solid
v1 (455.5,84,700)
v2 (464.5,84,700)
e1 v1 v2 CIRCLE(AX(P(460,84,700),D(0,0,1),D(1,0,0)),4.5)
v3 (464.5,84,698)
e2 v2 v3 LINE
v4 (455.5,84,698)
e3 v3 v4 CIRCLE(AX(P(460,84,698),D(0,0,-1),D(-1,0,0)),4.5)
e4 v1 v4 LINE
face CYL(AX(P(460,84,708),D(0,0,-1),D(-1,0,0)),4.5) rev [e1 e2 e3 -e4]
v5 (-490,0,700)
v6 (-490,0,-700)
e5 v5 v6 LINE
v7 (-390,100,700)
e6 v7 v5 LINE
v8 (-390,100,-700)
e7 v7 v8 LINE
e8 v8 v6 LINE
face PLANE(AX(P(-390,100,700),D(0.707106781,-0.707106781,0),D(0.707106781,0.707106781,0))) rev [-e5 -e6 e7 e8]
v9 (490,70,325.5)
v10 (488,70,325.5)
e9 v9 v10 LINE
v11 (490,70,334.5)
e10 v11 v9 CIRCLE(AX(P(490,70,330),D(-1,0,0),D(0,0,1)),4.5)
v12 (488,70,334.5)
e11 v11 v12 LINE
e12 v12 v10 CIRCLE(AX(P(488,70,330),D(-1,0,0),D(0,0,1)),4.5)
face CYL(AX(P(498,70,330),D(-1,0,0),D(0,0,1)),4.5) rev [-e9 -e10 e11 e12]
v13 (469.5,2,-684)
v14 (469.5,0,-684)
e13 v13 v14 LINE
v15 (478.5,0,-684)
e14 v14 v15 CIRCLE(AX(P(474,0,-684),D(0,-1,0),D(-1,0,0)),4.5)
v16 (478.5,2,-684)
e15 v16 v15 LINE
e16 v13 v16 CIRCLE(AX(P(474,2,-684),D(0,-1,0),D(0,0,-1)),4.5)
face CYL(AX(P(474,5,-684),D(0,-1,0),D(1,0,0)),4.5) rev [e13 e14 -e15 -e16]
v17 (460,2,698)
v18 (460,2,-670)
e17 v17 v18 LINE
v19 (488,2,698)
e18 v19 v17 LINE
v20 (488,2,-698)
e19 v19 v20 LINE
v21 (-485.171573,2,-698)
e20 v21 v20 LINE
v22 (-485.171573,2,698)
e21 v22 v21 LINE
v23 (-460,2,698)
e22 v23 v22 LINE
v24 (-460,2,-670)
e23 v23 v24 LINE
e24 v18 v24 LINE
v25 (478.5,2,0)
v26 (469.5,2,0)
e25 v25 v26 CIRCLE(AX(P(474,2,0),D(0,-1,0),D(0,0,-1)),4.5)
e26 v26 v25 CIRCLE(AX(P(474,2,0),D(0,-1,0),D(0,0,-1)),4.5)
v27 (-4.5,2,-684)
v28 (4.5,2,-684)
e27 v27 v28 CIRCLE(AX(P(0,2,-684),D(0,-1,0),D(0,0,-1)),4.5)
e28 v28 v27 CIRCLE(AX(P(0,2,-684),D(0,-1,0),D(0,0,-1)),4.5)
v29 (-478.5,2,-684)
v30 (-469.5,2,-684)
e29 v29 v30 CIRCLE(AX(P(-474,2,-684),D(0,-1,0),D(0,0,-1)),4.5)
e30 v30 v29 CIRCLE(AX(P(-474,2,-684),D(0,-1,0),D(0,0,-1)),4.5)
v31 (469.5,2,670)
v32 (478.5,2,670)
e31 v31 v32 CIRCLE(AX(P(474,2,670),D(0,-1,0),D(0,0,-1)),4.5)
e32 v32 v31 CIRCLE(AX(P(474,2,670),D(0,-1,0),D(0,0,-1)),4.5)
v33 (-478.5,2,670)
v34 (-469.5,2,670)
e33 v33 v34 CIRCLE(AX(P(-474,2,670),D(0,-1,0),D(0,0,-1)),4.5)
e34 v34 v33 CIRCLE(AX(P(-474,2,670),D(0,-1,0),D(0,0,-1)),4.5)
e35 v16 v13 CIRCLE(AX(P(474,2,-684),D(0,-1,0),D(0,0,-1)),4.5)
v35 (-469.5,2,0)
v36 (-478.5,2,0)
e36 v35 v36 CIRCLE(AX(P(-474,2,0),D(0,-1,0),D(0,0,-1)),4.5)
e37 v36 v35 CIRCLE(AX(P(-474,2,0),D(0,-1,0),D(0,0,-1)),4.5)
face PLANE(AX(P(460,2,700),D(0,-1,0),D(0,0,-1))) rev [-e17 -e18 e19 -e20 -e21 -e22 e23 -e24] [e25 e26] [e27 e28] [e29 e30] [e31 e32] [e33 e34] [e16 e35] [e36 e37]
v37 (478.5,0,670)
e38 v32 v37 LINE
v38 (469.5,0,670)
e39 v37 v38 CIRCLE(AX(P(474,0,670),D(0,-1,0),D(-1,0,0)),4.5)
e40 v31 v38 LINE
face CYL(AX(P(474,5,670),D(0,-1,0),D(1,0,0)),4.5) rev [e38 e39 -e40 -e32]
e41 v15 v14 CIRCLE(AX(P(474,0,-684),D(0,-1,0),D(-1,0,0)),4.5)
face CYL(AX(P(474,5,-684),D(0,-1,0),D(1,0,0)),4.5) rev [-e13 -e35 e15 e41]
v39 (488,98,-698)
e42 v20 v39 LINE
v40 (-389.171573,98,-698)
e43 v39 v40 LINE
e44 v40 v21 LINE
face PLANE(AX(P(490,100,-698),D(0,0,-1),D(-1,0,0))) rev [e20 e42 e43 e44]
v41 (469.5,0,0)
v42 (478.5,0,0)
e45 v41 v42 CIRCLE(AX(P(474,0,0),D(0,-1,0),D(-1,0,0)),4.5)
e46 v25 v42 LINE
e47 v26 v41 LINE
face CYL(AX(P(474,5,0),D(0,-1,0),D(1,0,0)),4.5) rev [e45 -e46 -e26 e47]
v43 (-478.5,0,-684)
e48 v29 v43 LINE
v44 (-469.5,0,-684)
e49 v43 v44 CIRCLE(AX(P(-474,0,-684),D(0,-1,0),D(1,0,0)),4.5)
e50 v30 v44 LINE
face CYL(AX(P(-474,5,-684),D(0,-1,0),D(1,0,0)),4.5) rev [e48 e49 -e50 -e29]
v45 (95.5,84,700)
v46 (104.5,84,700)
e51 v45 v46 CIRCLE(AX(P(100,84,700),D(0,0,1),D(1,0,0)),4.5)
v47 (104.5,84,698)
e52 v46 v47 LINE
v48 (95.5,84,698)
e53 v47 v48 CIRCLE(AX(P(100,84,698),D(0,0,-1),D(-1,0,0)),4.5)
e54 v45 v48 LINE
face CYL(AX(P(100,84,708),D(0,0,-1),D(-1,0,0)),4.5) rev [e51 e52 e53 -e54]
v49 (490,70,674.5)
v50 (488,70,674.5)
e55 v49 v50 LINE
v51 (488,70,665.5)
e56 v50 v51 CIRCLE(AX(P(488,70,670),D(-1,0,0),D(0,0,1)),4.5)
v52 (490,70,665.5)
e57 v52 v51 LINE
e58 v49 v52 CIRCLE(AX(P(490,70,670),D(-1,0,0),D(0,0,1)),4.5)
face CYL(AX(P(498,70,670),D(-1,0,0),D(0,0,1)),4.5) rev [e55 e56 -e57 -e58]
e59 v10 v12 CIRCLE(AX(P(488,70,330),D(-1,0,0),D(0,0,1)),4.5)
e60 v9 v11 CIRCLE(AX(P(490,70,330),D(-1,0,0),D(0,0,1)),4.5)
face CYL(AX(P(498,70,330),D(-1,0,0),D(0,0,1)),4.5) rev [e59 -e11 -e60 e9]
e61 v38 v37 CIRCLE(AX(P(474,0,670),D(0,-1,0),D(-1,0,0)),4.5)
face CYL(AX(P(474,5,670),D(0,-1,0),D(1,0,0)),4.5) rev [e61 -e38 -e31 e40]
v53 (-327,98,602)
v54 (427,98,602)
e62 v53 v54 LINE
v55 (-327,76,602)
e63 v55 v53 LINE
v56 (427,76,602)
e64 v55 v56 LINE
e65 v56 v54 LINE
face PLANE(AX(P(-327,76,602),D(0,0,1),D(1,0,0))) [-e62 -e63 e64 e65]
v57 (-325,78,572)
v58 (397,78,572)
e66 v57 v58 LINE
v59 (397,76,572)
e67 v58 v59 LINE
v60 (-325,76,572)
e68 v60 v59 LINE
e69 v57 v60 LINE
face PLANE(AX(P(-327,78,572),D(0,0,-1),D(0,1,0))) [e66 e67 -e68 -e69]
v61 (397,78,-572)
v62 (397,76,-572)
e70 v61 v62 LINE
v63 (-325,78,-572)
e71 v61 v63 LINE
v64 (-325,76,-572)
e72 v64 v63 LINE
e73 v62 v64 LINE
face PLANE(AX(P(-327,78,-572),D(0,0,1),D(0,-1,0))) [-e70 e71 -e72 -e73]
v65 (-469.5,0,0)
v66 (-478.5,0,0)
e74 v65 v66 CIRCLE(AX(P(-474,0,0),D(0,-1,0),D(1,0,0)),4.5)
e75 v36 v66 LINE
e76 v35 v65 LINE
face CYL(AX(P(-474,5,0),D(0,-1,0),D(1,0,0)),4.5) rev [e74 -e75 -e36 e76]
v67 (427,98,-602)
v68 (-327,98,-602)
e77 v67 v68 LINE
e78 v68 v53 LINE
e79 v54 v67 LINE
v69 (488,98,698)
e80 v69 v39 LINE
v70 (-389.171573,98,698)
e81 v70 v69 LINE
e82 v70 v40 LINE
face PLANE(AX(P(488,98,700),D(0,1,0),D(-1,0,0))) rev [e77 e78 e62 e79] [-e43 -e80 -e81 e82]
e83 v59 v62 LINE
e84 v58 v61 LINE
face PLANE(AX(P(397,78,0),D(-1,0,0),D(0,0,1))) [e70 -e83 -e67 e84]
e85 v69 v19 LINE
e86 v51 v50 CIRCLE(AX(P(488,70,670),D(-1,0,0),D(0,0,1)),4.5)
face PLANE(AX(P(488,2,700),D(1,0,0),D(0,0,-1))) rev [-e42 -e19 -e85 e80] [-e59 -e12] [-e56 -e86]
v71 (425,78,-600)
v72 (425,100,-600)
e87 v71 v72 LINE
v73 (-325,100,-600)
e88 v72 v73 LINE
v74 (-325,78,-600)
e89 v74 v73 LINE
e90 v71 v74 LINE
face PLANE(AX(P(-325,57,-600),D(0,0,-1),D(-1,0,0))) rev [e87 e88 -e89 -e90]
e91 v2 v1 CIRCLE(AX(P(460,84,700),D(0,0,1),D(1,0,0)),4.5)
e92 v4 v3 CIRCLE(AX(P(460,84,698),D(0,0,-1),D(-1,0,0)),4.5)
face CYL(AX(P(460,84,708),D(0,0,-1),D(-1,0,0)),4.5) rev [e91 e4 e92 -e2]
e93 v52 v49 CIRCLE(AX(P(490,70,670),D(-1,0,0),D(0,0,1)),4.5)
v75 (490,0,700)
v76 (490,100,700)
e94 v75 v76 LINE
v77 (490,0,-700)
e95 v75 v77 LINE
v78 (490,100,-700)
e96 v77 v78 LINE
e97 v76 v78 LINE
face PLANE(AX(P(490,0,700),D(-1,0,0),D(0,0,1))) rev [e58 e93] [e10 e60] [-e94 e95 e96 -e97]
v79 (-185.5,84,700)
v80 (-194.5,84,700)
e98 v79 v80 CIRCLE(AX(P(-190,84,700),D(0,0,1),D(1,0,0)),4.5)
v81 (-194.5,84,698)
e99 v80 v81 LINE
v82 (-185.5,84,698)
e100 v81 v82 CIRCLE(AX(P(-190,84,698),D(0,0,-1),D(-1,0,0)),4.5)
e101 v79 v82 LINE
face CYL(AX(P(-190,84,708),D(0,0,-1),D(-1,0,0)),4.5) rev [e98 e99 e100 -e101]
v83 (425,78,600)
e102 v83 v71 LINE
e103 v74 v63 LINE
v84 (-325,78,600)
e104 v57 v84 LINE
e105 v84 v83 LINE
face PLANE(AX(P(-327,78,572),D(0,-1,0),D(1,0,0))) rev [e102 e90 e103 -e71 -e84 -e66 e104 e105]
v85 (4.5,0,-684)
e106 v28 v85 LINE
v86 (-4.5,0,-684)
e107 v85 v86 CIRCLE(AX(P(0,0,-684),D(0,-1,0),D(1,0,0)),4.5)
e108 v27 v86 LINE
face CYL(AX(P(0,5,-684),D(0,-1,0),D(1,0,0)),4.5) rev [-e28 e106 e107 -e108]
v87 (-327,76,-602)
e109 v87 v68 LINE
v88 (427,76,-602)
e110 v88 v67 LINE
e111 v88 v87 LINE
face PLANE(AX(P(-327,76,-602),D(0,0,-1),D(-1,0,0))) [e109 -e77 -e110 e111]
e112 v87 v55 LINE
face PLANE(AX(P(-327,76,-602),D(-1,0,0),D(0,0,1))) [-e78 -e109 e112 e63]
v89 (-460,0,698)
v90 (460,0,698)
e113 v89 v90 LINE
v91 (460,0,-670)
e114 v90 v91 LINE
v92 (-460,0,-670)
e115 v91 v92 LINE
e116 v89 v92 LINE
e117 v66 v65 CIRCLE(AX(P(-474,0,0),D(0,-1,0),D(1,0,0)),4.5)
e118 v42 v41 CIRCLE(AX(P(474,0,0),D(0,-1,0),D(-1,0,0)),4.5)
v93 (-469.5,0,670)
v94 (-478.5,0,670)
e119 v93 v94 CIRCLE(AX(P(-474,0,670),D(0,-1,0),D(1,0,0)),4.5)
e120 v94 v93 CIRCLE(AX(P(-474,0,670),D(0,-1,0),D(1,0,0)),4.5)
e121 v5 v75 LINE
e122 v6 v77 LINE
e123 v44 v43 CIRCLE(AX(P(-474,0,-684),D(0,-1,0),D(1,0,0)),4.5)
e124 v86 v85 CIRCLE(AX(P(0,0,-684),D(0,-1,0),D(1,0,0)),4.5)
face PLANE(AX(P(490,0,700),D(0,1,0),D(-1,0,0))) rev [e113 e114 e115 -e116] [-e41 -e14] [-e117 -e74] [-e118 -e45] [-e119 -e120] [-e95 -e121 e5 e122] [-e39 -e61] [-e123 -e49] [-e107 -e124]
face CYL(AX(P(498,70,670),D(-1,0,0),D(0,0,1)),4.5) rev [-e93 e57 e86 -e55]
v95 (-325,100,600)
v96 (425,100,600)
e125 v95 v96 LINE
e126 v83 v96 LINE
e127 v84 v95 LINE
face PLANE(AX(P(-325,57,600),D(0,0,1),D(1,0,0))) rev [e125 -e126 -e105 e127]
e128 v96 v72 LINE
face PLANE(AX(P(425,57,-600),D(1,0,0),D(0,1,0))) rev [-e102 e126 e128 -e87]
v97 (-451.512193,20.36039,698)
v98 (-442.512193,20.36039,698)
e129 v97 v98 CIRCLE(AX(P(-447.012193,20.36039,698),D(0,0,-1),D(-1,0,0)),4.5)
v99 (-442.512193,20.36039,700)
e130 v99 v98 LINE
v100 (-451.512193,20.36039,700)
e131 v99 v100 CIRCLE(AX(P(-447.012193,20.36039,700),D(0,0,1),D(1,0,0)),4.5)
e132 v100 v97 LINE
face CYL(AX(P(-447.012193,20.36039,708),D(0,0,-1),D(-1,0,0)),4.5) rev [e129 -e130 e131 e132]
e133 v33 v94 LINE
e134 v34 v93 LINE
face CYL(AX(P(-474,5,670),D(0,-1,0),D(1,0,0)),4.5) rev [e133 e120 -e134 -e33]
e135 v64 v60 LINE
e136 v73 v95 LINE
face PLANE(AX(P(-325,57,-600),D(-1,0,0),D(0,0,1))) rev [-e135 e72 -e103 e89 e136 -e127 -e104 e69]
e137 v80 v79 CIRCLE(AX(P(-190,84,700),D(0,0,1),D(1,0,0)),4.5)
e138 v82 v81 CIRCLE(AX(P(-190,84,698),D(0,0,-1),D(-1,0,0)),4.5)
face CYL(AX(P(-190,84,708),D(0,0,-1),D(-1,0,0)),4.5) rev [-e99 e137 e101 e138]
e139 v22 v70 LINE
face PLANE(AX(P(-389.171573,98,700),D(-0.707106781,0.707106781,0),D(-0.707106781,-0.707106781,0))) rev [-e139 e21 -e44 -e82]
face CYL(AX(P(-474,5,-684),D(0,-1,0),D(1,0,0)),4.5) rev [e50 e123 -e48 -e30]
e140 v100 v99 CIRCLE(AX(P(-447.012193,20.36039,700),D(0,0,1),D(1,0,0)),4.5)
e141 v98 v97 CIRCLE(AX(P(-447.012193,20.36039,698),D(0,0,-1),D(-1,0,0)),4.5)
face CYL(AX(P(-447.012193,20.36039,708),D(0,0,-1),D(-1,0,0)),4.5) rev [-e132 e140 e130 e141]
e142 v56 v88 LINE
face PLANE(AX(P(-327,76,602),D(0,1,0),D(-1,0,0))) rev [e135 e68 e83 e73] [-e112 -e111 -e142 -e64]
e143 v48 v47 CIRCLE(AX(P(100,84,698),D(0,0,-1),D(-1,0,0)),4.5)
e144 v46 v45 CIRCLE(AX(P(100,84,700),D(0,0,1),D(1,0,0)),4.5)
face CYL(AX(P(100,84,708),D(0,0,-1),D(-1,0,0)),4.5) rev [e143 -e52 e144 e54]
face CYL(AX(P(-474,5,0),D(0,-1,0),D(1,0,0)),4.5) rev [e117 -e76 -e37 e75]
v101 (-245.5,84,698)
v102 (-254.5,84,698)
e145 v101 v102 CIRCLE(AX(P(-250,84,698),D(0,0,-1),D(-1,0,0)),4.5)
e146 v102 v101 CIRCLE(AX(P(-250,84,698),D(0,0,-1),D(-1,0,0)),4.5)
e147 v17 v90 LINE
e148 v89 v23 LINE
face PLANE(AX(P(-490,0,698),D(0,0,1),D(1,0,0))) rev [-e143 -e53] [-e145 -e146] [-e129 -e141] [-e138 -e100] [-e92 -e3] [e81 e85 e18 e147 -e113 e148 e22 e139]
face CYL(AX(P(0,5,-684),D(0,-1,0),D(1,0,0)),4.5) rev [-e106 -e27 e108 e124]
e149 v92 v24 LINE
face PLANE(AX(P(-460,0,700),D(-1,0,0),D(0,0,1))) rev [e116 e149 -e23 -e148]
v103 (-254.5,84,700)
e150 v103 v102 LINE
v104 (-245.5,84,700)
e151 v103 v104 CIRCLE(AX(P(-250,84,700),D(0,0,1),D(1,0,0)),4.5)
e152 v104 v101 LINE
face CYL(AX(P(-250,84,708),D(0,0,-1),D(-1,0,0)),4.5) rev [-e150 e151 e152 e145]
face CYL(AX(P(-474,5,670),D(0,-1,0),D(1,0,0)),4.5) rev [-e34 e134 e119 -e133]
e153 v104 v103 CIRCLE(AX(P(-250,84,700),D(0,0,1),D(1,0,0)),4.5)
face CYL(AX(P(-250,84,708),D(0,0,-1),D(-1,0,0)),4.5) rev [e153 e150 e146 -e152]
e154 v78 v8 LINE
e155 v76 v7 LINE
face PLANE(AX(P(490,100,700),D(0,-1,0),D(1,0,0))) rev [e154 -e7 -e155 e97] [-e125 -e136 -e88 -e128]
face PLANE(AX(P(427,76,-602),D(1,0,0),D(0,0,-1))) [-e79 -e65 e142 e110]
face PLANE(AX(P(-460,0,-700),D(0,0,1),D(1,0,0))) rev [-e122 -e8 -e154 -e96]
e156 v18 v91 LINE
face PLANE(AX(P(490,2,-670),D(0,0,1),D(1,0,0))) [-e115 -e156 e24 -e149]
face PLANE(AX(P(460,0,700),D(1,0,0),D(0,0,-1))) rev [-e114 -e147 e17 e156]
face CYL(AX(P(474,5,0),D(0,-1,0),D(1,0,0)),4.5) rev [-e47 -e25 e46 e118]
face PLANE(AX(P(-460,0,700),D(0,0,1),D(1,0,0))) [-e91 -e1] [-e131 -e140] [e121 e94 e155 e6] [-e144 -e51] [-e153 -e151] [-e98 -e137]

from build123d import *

# Parameters (mm, degrees)
EXTRUDE_1_DEPTH     = 700
SKETCH_2_W          = 750
SKETCH_2_H          = 1200
CUT_EXTRUDE_1_DEPTH = 43
SKETCH_3_W          = 754
SKETCH_3_H          = 1204
SKETCH_3_W_2        = 750
SKETCH_3_H_2        = 1200
EXTRUDE_2_DEPTH     = 24
EXTRUDE_3_DEPTH     = 2
EXTRUDE_4_DEPTH     = 2
SKETCH_6_W          = 980
SKETCH_6_H          = 30
EXTRUDE_5_DEPTH     = 2
EXTRUDE_7_DEPTH     = 2
SKETCH_9_R          = 4.5
CUT_EXTRUDE_2_DEPTH = 10
CUT_EXTRUDE_3_DEPTH = 45
SKETCH_11_R         = 4.5
CUT_EXTRUDE_4_DEPTH = 5
SKETCH_12_R         = 4.5
CUT_EXTRUDE_5_DEPTH = 10


with BuildPart() as part:
    # 草图1 → 凸台-拉伸1 (new, symmetric)
    with BuildSketch(Plane.XY):
        Polygon((490, 0), (460, 0), (460, 2), (488, 2), (488, 98), (-389.171572875, 98), (-485.171572875, 2), (-460, 2), (-460, 0), (-490, 0), (-390, 100), (490, 100), align=None)
    extrude(amount=EXTRUDE_1_DEPTH, both=True)

    # 草图2 → 切除-拉伸1 (cut)
    with BuildSketch(Plane(origin=(0, 100, 0), x_dir=(1, 0, 0), z_dir=(0, 1, 0))):
        with Locations((50, 0)):
            Rectangle(SKETCH_2_W, SKETCH_2_H)
    extrude(amount=-CUT_EXTRUDE_1_DEPTH, mode=Mode.SUBTRACT)

    # 草图3 → 凸台-拉伸2 (add)
    with BuildSketch(Plane(origin=(0, 100, 0), x_dir=(1, 0, 0), z_dir=(0, 1, 0))):
        with Locations((50, 0)):
            Rectangle(SKETCH_3_W, SKETCH_3_H)
        with Locations((50, 0)):
            Rectangle(SKETCH_3_W_2, SKETCH_3_H_2, mode=Mode.SUBTRACT)
    extrude(amount=-EXTRUDE_2_DEPTH)

    # 草图4 → 凸台-拉伸3 (add)
    with BuildSketch(Plane.XZ.offset(-76)):
        Polygon((-327, 602), (427, 602), (427, 572), (427, -572), (427, -602), (-327, -602), (-327, -572), (397, -572), (397, 0), (397, 572), (-327, 572), align=None)
    extrude(amount=-EXTRUDE_3_DEPTH)



with BuildPart() as body_2:
    # 草图5 → 凸台-拉伸4 (new body)
    with BuildSketch(Plane(origin=(0, 0, -700), x_dir=(-1, 0, 0), z_dir=(0, 0, -1))):
        Polygon((-490, 100), (-490, 0), (490, 0), (390, 100), align=None)
    extrude(amount=-EXTRUDE_4_DEPTH)


with BuildPart() as part_1:
    add(part.part)

    add(body_2.part)  # 凸台-拉伸5 merges body 2
    # 草图6 → 凸台-拉伸5 (add)
    with BuildSketch(Plane.XZ):
        with Locations((0, -685)):
            Rectangle(SKETCH_6_W, SKETCH_6_H)
    extrude(amount=-EXTRUDE_5_DEPTH)

    # 草图8 → 凸台-拉伸7 (add)
    with BuildSketch(Plane.XY.offset(700)):
        Polygon((490, 0), (490, 100), (-390, 100), (-490, 0), (-460, 0), (460, 0), align=None)
    extrude(amount=-EXTRUDE_7_DEPTH)

    # 草图9 → 切除-拉伸2 (cut)
    with BuildSketch(Plane(origin=(0, 0, 698), x_dir=(-1, 0, 0), z_dir=(0, 0, -1))):
        with Locations((-460, 84)):
            Circle(SKETCH_9_R)
        with Locations((250, 84)):
            Circle(SKETCH_9_R)
        with Locations((190, 84)):
            Circle(SKETCH_9_R)
        with Locations((447.012193309, 20.360389693)):
            Circle(SKETCH_9_R)
        with Locations((-100, 84)):
            Circle(SKETCH_9_R)
    extrude(amount=-CUT_EXTRUDE_2_DEPTH, mode=Mode.SUBTRACT)

    # 草图10 → 切除-拉伸3 (cut)
    with BuildSketch(Plane(origin=(0, 0, -700), x_dir=(-1, 0, 0), z_dir=(0, 0, -1))):
        Polygon((478.109799219, 11.890200781), (488, 2), (495.020614582, -5.020614582), (488.781283968, 5.695100391), align=None)
    extrude(amount=-CUT_EXTRUDE_3_DEPTH, mode=Mode.SUBTRACT)

    # 草图11 → 切除-拉伸4 (cut)
    with BuildSketch(Plane.XZ):
        with Locations((-474, 670)):
            Circle(SKETCH_11_R)
        with Locations((-474, 0)):
            Circle(SKETCH_11_R)
        with Locations((-474, -684)):
            Circle(SKETCH_11_R)
        with Locations((0, -684)):
            Circle(SKETCH_11_R)
        with Locations(Location((474, -684, 0), (0, 0, 270))):
            Circle(SKETCH_11_R)
        with Locations(Location((474, 0, 0), (0, 0, 270))):
            Circle(SKETCH_11_R)
        with Locations(Location((474, 670, 0), (0, 0, 270))):
            Circle(SKETCH_11_R)
    extrude(amount=-CUT_EXTRUDE_4_DEPTH, mode=Mode.SUBTRACT)

    # 草图12 → 切除-拉伸5 (cut)
    with BuildSketch(Plane.ZY.offset(-488)):
        with Locations((670, 70)):
            Circle(SKETCH_12_R)
        with Locations((330, 70)):
            Circle(SKETCH_12_R)
    extrude(amount=-CUT_EXTRUDE_5_DEPTH, mode=Mode.SUBTRACT)


solid = part_1.part
